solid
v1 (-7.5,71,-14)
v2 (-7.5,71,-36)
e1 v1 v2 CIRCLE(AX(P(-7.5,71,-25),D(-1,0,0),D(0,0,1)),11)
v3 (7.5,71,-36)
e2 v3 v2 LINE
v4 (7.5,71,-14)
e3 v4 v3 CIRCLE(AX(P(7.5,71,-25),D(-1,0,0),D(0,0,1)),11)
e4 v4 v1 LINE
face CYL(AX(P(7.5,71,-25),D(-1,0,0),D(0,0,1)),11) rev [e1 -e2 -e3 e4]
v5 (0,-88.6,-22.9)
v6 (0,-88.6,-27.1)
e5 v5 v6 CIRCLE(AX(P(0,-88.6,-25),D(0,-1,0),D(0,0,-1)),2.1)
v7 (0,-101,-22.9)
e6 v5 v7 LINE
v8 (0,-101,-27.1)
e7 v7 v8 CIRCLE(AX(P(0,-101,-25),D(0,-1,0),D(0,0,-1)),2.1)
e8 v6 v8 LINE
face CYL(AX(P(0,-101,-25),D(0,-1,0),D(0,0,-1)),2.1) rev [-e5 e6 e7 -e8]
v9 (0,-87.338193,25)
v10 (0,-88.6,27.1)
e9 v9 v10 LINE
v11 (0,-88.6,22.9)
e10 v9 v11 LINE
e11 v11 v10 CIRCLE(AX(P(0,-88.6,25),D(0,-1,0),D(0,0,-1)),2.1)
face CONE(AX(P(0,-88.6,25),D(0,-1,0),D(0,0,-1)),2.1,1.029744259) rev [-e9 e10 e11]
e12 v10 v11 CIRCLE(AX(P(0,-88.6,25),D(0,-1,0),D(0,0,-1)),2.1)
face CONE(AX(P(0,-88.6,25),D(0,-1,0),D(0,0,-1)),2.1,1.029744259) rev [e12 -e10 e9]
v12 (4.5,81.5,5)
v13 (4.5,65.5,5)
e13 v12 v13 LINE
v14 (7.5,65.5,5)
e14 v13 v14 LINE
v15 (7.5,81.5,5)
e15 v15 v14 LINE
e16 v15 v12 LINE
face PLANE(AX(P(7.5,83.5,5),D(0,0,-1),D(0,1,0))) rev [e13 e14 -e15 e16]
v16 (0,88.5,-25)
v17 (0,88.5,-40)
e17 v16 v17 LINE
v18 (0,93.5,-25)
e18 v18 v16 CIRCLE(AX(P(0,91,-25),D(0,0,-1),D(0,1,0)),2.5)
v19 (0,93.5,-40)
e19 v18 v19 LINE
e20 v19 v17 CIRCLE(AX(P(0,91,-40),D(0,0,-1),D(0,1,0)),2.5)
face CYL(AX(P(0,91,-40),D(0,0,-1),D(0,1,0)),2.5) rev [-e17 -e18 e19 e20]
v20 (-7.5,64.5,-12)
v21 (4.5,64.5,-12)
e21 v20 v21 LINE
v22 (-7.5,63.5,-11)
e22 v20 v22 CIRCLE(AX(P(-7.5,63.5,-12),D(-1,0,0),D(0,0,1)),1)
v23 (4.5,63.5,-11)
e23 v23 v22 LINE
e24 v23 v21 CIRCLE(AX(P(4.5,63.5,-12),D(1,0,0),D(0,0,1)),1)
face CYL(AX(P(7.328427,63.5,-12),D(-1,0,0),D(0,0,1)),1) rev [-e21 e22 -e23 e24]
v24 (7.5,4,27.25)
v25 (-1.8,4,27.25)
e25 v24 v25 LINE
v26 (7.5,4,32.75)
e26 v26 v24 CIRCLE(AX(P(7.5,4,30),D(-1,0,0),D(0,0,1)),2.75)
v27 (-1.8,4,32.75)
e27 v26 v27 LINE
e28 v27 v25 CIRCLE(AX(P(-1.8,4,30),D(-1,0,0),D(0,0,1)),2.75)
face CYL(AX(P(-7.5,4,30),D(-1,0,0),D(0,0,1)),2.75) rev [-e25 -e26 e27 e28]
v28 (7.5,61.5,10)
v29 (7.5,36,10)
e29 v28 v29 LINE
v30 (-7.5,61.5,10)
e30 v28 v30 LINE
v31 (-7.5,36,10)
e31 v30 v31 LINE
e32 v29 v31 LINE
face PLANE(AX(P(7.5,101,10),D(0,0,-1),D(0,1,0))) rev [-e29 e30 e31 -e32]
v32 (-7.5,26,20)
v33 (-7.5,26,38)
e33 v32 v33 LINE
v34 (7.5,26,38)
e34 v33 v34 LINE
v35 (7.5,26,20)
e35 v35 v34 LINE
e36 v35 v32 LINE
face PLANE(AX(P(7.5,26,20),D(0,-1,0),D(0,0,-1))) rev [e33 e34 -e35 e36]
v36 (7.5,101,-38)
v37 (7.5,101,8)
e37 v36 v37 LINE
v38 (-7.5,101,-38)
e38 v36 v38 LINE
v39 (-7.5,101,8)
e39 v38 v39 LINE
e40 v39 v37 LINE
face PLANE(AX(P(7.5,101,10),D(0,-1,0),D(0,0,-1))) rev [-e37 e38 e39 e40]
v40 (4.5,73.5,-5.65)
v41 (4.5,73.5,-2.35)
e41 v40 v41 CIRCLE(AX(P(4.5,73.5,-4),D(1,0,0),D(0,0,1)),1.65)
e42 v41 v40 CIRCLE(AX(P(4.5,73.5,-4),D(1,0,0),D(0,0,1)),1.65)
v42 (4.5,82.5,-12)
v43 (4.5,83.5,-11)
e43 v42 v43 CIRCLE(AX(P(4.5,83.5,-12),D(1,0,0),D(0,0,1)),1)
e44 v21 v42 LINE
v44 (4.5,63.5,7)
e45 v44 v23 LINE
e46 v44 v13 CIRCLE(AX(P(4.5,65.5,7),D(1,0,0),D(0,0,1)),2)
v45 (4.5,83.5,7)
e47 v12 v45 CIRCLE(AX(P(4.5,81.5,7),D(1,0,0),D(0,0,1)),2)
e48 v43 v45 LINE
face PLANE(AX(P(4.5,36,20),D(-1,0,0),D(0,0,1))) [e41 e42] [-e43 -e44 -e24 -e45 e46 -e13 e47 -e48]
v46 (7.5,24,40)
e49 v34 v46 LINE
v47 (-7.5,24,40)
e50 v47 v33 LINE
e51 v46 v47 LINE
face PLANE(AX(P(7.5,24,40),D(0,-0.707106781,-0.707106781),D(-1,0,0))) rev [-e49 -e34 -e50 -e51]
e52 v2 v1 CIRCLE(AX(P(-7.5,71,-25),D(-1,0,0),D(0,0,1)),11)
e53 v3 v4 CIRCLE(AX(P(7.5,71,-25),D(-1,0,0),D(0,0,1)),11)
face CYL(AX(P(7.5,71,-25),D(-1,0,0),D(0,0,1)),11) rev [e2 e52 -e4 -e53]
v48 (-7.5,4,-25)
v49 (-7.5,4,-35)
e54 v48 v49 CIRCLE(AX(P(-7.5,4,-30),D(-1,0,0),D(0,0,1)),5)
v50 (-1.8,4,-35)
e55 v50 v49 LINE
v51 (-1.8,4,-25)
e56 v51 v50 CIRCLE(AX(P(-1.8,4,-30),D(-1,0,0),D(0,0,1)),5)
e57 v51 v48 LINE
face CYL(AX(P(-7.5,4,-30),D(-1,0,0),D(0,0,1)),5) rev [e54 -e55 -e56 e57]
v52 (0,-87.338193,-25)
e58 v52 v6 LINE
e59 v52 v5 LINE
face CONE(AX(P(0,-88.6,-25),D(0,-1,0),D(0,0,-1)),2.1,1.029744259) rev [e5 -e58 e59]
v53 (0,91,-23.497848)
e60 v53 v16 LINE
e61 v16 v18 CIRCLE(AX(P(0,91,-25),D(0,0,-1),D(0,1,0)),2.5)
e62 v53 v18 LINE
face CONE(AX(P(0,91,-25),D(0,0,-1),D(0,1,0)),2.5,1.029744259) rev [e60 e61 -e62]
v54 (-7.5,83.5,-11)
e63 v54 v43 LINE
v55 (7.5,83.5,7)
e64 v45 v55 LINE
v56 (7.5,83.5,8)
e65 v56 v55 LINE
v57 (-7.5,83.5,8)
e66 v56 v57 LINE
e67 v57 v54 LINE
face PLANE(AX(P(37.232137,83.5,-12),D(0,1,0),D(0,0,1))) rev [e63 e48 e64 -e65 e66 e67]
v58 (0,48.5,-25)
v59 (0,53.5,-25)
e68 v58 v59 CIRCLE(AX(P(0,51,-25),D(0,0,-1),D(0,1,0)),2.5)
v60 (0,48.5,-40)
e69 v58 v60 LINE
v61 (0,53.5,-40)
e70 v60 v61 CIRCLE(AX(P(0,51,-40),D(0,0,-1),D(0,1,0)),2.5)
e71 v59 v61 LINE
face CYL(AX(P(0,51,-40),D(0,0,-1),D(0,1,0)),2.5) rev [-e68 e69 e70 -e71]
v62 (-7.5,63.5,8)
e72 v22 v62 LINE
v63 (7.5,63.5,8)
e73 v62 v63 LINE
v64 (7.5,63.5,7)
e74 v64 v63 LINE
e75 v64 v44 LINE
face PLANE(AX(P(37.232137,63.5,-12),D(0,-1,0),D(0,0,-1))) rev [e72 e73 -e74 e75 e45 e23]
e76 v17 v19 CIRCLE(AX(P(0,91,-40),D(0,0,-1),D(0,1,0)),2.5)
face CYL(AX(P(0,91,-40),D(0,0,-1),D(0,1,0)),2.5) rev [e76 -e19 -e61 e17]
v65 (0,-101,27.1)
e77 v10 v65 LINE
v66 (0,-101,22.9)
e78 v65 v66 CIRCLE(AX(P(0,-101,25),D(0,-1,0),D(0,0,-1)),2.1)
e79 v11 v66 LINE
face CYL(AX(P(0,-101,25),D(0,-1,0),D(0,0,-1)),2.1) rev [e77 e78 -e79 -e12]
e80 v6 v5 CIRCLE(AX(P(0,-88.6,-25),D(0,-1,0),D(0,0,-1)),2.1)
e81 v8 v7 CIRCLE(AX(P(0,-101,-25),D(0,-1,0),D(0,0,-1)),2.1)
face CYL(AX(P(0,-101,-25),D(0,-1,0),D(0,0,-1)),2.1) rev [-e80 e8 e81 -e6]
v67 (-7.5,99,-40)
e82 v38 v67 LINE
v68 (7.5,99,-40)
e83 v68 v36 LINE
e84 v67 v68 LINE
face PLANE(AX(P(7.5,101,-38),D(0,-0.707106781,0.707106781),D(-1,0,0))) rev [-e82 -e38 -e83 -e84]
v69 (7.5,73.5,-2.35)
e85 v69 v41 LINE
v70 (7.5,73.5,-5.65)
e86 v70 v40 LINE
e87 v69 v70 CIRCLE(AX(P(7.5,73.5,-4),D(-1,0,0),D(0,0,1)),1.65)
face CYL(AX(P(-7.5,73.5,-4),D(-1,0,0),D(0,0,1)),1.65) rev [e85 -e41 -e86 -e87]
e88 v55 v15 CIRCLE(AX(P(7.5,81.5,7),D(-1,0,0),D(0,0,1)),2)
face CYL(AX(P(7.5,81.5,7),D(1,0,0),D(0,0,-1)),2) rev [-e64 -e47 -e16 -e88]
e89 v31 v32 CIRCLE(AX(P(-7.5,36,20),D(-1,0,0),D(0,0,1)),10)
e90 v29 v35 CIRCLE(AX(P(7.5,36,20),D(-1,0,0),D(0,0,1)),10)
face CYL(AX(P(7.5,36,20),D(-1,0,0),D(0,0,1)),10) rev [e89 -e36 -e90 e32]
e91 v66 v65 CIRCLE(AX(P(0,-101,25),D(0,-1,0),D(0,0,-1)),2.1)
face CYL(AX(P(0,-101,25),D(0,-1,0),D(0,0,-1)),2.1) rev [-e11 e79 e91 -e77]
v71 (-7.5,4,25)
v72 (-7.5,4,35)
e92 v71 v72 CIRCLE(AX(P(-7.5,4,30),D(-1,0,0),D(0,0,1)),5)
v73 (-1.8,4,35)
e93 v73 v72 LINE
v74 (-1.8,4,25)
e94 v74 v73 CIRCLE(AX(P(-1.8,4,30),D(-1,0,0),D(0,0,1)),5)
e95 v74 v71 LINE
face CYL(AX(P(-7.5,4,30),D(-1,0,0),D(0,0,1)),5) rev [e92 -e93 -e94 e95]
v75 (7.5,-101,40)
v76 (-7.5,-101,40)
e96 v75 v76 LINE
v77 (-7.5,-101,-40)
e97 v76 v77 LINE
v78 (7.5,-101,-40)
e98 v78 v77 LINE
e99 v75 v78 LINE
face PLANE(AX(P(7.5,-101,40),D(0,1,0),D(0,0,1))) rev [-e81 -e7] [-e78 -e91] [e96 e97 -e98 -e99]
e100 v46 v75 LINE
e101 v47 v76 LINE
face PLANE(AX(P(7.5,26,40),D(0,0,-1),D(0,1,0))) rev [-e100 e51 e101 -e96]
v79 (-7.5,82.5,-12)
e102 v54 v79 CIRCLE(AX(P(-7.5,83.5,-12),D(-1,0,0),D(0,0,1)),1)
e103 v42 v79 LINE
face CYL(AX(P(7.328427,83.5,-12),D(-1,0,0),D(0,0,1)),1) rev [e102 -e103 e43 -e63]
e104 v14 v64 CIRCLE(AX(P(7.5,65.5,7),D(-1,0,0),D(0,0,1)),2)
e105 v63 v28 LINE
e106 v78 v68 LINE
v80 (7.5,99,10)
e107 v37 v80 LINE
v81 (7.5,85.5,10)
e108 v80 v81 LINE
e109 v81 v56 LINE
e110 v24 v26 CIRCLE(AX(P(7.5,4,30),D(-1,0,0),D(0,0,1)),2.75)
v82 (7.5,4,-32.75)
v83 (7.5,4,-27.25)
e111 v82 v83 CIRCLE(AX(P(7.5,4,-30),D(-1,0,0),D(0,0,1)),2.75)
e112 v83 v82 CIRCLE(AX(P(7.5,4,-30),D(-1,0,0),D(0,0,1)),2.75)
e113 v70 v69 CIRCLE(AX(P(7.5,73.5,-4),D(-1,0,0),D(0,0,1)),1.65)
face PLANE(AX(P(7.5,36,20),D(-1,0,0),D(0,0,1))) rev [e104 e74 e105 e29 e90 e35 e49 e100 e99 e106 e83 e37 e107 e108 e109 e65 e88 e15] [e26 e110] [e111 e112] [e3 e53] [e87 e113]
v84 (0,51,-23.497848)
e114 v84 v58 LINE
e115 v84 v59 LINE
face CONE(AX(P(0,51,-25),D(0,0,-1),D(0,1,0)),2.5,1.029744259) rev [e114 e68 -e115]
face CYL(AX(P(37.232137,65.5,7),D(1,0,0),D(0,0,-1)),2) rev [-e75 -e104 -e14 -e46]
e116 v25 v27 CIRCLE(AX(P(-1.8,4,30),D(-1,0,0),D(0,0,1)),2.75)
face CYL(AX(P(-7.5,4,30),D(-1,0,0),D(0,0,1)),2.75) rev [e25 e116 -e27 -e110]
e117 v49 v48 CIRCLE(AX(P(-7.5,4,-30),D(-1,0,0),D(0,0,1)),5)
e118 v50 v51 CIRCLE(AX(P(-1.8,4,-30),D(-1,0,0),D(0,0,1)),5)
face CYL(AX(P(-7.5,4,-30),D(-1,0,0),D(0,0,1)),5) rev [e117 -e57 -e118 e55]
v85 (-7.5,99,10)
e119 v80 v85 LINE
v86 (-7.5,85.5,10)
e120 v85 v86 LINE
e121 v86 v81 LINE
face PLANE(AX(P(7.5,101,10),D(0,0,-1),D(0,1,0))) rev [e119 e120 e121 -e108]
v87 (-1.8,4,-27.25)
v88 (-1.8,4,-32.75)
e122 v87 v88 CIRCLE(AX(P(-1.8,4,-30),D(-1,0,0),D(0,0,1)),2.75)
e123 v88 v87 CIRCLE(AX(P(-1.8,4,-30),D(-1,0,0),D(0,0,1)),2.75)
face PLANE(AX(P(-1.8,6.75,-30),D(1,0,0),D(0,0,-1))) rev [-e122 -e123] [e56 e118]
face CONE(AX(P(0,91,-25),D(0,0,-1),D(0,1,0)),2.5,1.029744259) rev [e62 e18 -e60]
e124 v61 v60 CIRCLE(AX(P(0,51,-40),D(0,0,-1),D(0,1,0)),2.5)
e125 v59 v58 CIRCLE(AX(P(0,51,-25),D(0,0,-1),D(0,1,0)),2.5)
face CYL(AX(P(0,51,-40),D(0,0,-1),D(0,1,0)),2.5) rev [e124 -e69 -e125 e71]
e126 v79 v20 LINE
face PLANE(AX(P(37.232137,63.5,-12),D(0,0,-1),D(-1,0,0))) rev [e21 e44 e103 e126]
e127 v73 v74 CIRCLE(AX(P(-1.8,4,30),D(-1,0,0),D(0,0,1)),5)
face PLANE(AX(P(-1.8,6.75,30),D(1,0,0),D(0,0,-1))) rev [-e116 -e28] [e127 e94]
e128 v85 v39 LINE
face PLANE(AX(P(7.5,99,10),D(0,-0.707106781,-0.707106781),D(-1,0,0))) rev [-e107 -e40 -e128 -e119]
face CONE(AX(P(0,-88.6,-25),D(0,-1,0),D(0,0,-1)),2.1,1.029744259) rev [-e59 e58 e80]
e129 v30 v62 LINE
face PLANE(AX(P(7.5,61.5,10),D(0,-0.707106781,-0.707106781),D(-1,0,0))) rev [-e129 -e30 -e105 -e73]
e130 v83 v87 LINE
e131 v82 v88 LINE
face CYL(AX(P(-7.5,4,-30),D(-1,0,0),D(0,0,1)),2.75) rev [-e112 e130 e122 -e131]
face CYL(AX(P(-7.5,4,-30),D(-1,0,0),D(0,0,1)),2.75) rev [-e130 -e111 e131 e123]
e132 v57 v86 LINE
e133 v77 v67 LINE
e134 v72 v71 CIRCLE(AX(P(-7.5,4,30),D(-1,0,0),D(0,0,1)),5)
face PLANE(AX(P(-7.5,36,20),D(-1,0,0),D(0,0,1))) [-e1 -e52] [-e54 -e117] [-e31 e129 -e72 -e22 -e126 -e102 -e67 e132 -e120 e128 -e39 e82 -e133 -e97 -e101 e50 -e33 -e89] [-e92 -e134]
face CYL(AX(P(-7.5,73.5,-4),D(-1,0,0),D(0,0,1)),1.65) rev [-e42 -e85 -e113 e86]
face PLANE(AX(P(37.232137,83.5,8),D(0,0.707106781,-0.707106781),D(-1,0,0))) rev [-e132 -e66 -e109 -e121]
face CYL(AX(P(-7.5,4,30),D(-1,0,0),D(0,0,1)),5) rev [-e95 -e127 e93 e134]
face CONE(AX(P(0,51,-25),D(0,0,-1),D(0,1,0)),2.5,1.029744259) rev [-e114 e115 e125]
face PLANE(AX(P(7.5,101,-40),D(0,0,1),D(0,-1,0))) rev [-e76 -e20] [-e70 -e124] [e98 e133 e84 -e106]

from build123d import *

# Parameters (mm, degrees)
EXTRUDE_1_DEPTH                = 7.5
SKETCH_2_R                     = 11
CUT_EXTRUDE_1_DEPTH            = 110.66312051
HOLE_WIZARD_M5_1_D             = 4.2
HOLE_WIZARD_M5_1_DEPTH         = 12.4
HOLE_WIZARD_M5_1_TIP           = 1.2618073
HOLE_WIZARD_M5_1_2_D           = 5.5
HOLE_WIZARD_M5_1_2_CBORE_D     = 10
HOLE_WIZARD_M5_1_2_CBORE_DEPTH = 5.7
HOLE_WIZARD_M6_1_D             = 5
HOLE_WIZARD_M6_1_DEPTH         = 15
HOLE_WIZARD_M6_1_TIP           = 1.502151548
CHAMFER_1_SIZE                 = 2
SKETCH_12_R                    = 2.5
CUT_EXTRUDE_2_DEPTH            = 110.66312051
HOLE_WIZARD_M4_1_D             = 3.3
SKETCH_15_W                    = 22
SKETCH_15_H                    = 20
CUT_EXTRUDE_3_DEPTH            = 12
SKETCH_16_W                    = 5
SKETCH_16_H                    = 20
CUT_EXTRUDE_4_DEPTH            = 110.293183685
SKETCH_17_R                    = 1
CUT_EXTRUDE_5_DEPTH            = 12
CHAMFER_2_SIZE                 = 2
FILLET_2_R                     = 2


with BuildPart() as part:
    # 草图1 → 凸台-拉伸1 (new, symmetric)
    with BuildSketch(Plane(origin=(0, 0, 0), x_dir=(0, 0, -1), z_dir=(1, 0, 0))):
        with BuildLine():
            Line((-10, 101), (-10, 36))
            ThreePointArc((-10, 36), (-12.928932188, 28.928932188), (-20, 26))
            Line((-20, 26), (-40, 26))
            Line((-40, 26), (-40, -101))
            Line((-40, -101), (40, -101))
            Line((40, -101), (40, 101))
            Line((40, 101), (-10, 101))
        make_face()
    extrude(amount=EXTRUDE_1_DEPTH, both=True)

    # 草图2 → 切除-拉伸1 (cut, through all)
    with BuildSketch(Plane.ZY.offset(7.5)):
        with Locations((-25, 71)):
            Circle(SKETCH_2_R)
    extrude(amount=-CUT_EXTRUDE_1_DEPTH, mode=Mode.SUBTRACT)

    # Hole Wizard M5 _1
    with Locations(Plane(origin=(0, -101, 0), x_dir=(-1, 0, 0), z_dir=(0, -1, 0))):
        with Locations((0, 25), (0, -25)):
            Hole(HOLE_WIZARD_M5_1_D / 2, depth=HOLE_WIZARD_M5_1_DEPTH)
            with Locations((0, 0, -(HOLE_WIZARD_M5_1_DEPTH + HOLE_WIZARD_M5_1_TIP / 2))):  # 118° drill point
                Cone(0, HOLE_WIZARD_M5_1_D / 2, HOLE_WIZARD_M5_1_TIP, mode=Mode.SUBTRACT)

    # Hole Wizard M5 _1 2 (through all)
    with Locations(Plane.ZY.offset(7.5)):
        with Locations((-30, 4), (30, 4)):
            CounterBoreHole(HOLE_WIZARD_M5_1_2_D / 2, HOLE_WIZARD_M5_1_2_CBORE_D / 2, HOLE_WIZARD_M5_1_2_CBORE_DEPTH)

    # M6 螺纹孔1
    with Locations(Plane(origin=(0, 0, -40), x_dir=(-1, 0, 0), z_dir=(0, 0, -1))):
        with Locations((0, 51), (0, 91)):
            Hole(HOLE_WIZARD_M6_1_D / 2, depth=HOLE_WIZARD_M6_1_DEPTH)
            with Locations((0, 0, -(HOLE_WIZARD_M6_1_DEPTH + HOLE_WIZARD_M6_1_TIP / 2))):  # 118° drill point
                Cone(0, HOLE_WIZARD_M6_1_D / 2, HOLE_WIZARD_M6_1_TIP, mode=Mode.SUBTRACT)

    # 倒角1
    chamfer_1_edges = [part.edges().sort_by_distance(p)[0] for p in [
        (0, 26, 40),
        (0, 101, 10),
        (0, 101, -40),
    ]]
    chamfer(chamfer_1_edges, length=CHAMFER_1_SIZE)

    # 草图12 → 切除-拉伸2 (cut, through all)
    with BuildSketch(Plane(origin=(7.5, 0, 0), x_dir=(0, 0, -1), z_dir=(1, 0, 0))):
        with Locations((-11, 73.5)):
            Circle(SKETCH_12_R)
    extrude(amount=-CUT_EXTRUDE_2_DEPTH, mode=Mode.SUBTRACT)

    # M4 螺纹孔1 (through all)
    with Locations(Plane.ZY.offset(7.5)):
        with Locations((-4, 73.5)):
            Hole(HOLE_WIZARD_M4_1_D / 2)

    # 草图15 → 切除-拉伸3 (cut)
    with BuildSketch(Plane.ZY.offset(7.5)):
        with Locations((-1, 73.5)):
            Rectangle(SKETCH_15_W, SKETCH_15_H)
    extrude(amount=-CUT_EXTRUDE_3_DEPTH, mode=Mode.SUBTRACT)

    # 草图16 → 切除-拉伸4 (cut, through all)
    with BuildSketch(Plane.ZY.offset(-4.5)):
        with Locations((7.5, 73.5)):
            Rectangle(SKETCH_16_W, SKETCH_16_H)
    extrude(amount=-CUT_EXTRUDE_4_DEPTH, mode=Mode.SUBTRACT)

    # 草图17 → 切除-拉伸5 (cut)
    with BuildSketch(Plane.ZY.offset(7.5)):
        with Locations((-12, 83.5)):
            Circle(SKETCH_17_R)
        with Locations((-12, 63.5)):
            Circle(SKETCH_17_R)
    extrude(amount=-CUT_EXTRUDE_5_DEPTH, mode=Mode.SUBTRACT)

    # 倒角2
    chamfer_2_edges = [part.edges().sort_by_distance(p)[0] for p in [
        (0, 83.5, 10),
        (0, 63.5, 10),
    ]]
    chamfer(chamfer_2_edges, length=CHAMFER_2_SIZE)

    # 圆角2
    fillet_2_edges = [part.edges().sort_by_distance(p)[0] for p in [
        (6, 63.5, 5),
        (6, 83.5, 5),
    ]]
    fillet(fillet_2_edges, radius=FILLET_2_R)


solid = part.part
